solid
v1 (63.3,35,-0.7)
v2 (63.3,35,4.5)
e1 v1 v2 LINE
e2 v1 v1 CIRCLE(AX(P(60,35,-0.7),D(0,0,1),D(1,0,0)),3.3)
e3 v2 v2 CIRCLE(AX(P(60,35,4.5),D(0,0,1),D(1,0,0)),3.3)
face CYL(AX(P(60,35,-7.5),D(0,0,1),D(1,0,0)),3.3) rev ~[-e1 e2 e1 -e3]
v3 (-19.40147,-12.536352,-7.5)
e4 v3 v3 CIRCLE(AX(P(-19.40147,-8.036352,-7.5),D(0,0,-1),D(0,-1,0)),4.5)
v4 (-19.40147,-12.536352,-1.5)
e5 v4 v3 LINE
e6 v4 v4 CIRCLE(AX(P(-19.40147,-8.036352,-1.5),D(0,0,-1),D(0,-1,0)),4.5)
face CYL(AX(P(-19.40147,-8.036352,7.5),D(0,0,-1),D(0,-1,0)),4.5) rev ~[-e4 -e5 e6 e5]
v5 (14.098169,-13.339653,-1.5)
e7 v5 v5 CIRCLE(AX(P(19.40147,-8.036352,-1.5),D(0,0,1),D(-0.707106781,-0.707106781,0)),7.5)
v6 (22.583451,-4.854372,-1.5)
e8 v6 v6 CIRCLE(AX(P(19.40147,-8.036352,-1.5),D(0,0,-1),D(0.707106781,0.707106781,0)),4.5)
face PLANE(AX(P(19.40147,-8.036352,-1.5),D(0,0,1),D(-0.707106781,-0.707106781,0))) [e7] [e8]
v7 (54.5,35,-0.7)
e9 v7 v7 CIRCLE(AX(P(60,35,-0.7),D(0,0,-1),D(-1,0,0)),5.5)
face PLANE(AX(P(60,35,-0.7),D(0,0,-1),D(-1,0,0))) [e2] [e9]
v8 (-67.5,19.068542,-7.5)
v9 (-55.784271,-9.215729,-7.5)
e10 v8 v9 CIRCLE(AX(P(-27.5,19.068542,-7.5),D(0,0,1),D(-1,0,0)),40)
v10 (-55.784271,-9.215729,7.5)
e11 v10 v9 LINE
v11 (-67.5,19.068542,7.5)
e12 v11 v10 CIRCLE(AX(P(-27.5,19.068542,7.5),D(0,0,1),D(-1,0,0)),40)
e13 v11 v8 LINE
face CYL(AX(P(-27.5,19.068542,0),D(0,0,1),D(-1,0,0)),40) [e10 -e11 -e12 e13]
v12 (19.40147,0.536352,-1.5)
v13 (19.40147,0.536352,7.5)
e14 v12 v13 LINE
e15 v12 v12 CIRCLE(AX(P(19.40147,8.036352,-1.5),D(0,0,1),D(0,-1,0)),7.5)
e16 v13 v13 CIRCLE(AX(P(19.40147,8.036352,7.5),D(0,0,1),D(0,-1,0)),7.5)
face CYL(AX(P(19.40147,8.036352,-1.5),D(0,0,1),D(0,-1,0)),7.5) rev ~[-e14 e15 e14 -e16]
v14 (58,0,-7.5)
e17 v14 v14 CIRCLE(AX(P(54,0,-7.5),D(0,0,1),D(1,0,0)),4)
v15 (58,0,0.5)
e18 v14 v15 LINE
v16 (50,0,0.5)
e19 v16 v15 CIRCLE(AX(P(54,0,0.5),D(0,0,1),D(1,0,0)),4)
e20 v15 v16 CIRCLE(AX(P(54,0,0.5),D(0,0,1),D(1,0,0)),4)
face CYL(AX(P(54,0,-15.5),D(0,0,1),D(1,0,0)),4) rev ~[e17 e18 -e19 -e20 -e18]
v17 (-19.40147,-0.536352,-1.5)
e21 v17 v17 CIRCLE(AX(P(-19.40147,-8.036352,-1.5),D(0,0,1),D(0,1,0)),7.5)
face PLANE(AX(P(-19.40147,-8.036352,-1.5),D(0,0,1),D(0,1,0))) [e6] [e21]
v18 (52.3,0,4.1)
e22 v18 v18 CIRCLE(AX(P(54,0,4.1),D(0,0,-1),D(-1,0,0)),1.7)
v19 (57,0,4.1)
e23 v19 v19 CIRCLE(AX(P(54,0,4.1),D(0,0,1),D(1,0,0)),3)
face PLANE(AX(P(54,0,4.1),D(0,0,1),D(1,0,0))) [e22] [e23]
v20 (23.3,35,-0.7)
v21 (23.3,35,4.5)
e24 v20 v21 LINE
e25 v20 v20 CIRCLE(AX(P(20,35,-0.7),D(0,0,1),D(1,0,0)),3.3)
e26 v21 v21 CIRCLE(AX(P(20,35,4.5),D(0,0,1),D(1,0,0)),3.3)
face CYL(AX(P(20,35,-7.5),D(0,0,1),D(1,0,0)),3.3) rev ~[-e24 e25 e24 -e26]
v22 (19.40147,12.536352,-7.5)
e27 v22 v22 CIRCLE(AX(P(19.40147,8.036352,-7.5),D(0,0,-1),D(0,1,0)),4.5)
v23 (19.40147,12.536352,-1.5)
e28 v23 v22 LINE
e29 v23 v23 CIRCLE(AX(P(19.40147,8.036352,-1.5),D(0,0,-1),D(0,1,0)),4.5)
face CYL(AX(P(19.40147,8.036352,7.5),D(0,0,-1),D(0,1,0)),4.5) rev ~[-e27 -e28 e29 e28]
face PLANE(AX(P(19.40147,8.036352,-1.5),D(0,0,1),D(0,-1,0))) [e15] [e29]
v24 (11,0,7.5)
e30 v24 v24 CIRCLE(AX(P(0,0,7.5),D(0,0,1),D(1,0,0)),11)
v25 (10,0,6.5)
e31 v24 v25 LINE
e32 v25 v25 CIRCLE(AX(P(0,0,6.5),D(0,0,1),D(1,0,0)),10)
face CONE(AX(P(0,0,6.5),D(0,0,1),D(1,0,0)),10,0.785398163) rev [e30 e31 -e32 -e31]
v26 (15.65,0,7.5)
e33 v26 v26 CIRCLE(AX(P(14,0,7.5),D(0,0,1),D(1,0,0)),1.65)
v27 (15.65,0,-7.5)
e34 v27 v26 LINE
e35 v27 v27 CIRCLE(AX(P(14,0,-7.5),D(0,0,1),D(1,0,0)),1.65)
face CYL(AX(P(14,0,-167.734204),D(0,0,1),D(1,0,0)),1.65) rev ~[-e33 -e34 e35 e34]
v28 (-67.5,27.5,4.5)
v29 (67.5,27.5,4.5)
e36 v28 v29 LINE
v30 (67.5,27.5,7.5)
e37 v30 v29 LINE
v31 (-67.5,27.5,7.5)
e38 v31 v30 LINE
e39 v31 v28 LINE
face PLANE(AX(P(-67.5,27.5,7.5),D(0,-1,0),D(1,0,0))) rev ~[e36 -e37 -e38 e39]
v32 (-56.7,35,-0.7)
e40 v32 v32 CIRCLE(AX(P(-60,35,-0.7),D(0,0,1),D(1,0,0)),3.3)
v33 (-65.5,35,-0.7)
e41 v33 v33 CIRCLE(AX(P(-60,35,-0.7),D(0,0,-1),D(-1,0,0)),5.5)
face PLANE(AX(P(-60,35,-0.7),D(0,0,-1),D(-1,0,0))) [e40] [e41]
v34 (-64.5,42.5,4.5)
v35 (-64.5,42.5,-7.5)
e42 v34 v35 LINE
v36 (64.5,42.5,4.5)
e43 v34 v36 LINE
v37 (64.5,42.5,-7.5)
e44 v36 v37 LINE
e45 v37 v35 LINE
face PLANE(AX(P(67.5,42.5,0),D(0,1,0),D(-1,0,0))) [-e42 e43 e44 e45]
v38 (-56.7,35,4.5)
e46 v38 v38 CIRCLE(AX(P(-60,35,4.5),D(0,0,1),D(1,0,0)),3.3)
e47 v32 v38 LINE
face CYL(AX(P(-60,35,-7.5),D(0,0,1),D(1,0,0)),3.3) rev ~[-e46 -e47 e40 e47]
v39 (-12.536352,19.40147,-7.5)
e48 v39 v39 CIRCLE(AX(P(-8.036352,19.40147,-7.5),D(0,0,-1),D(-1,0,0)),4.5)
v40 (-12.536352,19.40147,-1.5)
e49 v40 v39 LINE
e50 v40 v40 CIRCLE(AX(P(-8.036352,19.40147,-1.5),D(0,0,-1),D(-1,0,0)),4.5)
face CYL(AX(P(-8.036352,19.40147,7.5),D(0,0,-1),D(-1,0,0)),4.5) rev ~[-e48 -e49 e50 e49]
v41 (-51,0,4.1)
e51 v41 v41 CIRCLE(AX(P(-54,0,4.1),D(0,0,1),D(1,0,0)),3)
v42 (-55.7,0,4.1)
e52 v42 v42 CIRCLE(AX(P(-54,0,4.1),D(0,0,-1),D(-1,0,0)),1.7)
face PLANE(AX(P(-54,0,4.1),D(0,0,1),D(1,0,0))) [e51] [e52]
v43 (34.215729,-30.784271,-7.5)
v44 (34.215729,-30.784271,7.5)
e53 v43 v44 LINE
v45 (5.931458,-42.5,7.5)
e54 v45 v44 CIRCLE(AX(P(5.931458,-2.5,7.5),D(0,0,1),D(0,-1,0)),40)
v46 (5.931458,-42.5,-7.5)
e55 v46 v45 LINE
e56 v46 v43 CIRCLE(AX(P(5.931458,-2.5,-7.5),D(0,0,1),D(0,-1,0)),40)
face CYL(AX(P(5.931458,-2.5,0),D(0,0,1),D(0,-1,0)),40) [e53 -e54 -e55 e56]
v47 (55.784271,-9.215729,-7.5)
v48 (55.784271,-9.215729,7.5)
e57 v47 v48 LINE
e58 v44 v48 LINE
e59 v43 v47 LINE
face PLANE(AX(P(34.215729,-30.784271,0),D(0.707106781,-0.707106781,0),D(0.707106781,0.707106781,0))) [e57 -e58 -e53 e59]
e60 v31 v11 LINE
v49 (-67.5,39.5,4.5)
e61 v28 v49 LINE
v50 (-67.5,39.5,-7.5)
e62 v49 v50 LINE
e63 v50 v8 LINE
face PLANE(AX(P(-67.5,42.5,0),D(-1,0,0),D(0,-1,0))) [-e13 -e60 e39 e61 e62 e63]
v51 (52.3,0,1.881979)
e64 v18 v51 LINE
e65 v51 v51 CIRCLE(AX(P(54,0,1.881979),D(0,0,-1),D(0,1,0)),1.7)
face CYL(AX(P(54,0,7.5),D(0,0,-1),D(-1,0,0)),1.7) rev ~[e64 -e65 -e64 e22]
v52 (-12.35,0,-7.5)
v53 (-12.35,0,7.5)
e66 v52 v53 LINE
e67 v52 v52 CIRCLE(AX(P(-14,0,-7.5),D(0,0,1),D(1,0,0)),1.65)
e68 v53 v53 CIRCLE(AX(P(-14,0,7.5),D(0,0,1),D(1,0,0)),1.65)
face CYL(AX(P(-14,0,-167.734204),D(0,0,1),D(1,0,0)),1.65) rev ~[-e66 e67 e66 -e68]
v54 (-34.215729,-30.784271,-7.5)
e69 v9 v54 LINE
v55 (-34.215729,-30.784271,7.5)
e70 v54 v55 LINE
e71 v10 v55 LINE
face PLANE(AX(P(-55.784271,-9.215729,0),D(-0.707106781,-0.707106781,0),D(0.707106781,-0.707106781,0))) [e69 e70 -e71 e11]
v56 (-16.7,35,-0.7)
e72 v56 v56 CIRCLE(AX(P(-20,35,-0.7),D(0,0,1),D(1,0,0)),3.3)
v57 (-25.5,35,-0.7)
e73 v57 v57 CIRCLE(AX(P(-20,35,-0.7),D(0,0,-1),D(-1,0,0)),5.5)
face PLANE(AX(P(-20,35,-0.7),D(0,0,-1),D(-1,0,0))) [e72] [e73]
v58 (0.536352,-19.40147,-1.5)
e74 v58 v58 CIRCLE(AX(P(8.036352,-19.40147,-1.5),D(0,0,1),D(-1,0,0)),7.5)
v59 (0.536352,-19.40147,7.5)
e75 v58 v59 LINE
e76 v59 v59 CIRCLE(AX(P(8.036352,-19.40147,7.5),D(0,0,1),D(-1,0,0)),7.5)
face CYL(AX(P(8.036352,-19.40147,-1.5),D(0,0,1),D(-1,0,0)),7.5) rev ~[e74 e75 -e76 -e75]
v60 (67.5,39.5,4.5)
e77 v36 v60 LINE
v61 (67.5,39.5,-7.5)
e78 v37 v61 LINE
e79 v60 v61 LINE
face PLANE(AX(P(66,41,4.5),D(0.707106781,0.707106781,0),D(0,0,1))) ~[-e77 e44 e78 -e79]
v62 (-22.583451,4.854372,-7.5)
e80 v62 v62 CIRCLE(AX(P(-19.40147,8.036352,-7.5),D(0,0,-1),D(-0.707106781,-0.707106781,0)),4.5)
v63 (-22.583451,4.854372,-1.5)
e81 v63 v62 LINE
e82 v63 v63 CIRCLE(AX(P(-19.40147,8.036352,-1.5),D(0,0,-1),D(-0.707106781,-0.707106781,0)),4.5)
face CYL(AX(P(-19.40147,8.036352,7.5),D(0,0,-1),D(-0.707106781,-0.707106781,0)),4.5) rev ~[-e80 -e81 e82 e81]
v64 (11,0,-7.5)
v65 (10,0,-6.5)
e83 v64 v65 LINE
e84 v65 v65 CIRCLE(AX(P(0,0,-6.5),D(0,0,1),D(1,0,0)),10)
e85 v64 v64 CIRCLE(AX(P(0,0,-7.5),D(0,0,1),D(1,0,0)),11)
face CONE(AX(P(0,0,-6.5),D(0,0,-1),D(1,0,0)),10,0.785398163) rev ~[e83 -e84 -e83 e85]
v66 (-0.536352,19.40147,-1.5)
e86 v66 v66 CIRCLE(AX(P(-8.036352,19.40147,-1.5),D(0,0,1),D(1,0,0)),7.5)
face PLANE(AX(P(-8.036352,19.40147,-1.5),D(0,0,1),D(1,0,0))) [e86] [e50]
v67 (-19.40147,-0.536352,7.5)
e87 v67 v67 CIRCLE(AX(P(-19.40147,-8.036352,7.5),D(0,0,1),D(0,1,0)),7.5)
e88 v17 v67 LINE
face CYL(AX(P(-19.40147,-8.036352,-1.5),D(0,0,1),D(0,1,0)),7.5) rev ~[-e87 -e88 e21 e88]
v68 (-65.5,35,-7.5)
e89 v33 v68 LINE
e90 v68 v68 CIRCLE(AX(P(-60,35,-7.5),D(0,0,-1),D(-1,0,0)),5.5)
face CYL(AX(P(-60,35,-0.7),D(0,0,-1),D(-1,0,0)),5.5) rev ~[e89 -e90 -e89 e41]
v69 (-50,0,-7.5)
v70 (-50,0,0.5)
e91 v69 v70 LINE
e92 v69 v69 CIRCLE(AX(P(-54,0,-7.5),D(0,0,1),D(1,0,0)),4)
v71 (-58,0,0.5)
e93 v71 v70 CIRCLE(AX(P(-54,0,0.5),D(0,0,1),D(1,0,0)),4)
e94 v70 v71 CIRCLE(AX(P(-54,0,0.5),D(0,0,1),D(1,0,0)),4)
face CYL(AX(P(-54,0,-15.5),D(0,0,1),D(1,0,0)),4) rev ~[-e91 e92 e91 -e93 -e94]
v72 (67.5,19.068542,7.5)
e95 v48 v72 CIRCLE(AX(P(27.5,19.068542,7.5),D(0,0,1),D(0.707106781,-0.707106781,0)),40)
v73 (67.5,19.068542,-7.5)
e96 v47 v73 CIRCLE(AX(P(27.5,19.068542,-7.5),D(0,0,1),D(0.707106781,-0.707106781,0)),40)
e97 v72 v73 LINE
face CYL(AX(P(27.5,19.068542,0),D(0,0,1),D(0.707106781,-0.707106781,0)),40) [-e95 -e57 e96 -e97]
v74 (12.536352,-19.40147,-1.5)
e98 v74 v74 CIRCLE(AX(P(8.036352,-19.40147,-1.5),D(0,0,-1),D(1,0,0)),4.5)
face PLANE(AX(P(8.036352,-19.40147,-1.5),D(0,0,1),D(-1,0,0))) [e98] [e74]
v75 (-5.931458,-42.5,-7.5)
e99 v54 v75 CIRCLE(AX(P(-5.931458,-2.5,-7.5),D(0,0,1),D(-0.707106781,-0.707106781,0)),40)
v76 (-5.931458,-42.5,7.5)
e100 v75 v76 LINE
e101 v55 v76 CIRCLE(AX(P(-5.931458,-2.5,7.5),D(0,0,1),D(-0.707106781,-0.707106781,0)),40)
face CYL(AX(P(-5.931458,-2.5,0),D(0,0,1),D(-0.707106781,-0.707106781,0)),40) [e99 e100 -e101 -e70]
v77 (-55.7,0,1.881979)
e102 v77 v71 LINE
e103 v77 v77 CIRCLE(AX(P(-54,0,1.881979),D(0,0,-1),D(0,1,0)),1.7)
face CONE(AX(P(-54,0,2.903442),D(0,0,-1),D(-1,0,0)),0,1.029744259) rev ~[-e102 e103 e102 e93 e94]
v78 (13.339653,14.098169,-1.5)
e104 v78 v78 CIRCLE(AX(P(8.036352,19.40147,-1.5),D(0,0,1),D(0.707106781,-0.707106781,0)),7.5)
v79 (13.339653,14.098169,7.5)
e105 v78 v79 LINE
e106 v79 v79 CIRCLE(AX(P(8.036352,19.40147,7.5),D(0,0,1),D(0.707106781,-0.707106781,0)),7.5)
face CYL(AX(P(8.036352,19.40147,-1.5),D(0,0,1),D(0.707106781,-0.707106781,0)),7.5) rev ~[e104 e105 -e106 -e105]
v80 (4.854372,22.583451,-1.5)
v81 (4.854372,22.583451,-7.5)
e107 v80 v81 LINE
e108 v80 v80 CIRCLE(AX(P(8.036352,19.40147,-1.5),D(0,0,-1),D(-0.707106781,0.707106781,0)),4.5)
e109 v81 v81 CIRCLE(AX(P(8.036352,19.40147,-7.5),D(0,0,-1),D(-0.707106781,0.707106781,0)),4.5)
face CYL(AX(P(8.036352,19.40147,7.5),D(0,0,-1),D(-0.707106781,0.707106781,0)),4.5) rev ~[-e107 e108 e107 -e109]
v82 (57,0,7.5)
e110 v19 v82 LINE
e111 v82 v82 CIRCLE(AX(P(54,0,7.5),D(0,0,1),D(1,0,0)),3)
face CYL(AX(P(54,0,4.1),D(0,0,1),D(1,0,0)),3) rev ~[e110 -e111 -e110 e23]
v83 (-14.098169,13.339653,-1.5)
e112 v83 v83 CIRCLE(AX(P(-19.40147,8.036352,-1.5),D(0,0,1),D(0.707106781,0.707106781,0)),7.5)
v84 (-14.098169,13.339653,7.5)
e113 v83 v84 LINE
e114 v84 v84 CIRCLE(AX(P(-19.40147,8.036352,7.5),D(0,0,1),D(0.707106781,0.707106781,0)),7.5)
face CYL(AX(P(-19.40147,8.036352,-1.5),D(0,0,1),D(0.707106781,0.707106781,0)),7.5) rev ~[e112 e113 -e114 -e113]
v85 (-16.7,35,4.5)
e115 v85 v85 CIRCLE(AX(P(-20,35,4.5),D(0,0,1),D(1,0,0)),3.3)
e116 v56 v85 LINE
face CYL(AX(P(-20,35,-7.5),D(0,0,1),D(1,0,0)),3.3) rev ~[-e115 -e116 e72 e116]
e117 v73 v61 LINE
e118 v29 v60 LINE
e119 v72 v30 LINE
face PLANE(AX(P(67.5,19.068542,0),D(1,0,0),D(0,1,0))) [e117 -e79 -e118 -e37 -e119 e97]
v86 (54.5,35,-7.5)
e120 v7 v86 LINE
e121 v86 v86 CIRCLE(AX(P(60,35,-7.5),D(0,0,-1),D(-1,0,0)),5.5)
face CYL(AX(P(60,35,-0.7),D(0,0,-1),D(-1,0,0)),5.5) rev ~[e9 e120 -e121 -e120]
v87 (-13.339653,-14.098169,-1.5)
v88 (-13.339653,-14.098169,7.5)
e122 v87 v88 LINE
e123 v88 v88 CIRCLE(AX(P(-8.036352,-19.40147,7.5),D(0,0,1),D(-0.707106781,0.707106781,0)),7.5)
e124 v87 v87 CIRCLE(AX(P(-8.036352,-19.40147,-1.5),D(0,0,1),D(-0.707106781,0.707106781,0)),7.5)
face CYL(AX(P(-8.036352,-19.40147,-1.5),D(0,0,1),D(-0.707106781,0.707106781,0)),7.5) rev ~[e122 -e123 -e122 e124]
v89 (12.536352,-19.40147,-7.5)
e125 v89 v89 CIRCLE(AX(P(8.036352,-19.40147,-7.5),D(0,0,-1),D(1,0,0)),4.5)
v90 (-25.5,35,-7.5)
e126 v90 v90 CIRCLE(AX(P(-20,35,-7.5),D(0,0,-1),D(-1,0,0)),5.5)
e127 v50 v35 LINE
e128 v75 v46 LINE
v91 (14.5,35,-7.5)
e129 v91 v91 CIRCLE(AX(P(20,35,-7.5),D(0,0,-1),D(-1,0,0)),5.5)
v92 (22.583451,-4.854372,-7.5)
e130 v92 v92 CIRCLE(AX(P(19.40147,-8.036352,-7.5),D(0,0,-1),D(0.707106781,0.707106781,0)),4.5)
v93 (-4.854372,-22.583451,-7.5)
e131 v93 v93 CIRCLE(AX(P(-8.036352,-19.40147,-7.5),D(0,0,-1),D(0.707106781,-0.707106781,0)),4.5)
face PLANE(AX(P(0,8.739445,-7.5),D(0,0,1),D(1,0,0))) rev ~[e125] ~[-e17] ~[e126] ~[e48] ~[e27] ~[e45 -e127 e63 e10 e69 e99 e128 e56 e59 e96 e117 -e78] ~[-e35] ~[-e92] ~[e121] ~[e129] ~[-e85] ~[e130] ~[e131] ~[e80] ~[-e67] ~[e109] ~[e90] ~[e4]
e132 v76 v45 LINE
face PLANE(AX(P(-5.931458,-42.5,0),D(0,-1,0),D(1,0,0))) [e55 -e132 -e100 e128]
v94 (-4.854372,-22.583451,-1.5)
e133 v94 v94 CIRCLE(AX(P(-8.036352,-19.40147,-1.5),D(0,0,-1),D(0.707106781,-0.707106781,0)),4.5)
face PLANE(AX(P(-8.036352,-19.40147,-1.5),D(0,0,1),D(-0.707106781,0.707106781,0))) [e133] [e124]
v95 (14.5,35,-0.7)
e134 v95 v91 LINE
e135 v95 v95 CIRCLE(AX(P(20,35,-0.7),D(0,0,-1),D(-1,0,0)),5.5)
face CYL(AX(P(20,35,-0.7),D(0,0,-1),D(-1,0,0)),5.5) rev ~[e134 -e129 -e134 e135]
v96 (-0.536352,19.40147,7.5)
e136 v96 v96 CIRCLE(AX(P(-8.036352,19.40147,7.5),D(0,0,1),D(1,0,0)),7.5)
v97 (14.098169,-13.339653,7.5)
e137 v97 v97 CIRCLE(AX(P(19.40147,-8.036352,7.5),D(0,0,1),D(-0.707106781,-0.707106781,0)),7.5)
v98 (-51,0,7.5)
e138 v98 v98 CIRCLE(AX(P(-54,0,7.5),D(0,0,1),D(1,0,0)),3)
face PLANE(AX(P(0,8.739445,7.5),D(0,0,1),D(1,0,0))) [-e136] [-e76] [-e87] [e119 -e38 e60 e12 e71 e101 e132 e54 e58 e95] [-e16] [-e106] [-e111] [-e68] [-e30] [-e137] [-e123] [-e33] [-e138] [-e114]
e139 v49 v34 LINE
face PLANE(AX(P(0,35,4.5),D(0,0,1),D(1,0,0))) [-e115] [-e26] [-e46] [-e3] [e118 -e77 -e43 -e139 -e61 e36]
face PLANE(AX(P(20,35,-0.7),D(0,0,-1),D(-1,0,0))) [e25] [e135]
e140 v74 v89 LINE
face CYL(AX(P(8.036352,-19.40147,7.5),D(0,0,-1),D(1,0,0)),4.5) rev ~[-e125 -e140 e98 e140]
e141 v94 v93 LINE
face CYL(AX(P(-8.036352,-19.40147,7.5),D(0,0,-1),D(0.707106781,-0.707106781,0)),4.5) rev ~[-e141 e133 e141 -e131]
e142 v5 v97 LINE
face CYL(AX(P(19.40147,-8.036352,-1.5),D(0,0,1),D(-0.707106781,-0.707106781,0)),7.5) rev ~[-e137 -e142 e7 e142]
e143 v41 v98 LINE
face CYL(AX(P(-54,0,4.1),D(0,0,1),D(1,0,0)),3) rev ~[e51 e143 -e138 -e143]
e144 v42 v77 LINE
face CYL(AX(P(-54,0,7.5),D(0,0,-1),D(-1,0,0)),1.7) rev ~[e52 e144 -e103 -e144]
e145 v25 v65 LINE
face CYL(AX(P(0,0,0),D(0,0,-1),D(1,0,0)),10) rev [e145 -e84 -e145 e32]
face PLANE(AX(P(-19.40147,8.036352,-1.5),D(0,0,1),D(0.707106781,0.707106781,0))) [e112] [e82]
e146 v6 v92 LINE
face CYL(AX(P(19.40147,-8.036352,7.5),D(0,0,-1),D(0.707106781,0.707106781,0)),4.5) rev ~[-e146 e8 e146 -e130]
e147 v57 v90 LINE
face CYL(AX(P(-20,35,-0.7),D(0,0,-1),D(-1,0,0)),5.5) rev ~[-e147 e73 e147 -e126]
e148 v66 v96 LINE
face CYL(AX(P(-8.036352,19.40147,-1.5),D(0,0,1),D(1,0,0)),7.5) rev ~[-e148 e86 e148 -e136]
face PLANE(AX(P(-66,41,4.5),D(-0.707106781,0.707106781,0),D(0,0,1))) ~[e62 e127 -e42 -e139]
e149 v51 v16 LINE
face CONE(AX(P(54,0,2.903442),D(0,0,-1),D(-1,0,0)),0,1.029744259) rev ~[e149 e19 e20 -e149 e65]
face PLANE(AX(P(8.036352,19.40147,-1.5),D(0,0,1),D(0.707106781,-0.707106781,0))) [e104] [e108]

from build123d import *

# Parameters (mm, degrees)
SKETCH_1_R                  = 10
EXTRUDE_1_DEPTH             = 7.5
HOLE_WIZARD_2_D             = 9
HOLE_WIZARD_2_CBORE_D       = 15
HOLE_WIZARD_2_CBORE_DEPTH   = 9
CHAMFER_1_SIZE              = 1
PATTERN_CIRCULAR_1_COUNT    = 8
HOLE_WIZARD_2_2_D           = 3.4
HOLE_WIZARD_2_2_CBORE_D     = 6
HOLE_WIZARD_2_2_CBORE_DEPTH = 3.4
HOLE_WIZARD_8_0_8_1_D       = 8
HOLE_WIZARD_8_0_8_1_DEPTH   = 8
HOLE_WIZARD_8_0_8_1_TIP     = 2.403442476
HOLE_WIZARD_M4_1_D          = 3.3
SKETCH_10_W                 = 135
SKETCH_10_H                 = 15
CUT_EXTRUDE_1_DEPTH         = 3
HOLE_WIZARD_3_D             = 6.6
HOLE_WIZARD_3_CBORE_D       = 11
HOLE_WIZARD_3_CBORE_DEPTH   = 6.8
CHAMFER_2_SIZE              = 3


with BuildPart() as part:
    # 草图1 → 凸台-拉伸1 (new, symmetric)
    with BuildSketch(Plane.XY):
        with BuildLine():
            Line((-55.784271247, -9.215728753), (-34.215728753, -30.784271247))
            ThreePointArc((-34.215728753, -30.784271247), (-21.2387948, -39.4551813), (-5.931457505, -42.5))
            Line((-5.931457505, -42.5), (5.931457505, -42.5))
            ThreePointArc((5.931457505, -42.5), (21.2387948, -39.4551813), (34.215728753, -30.784271247))
            Line((34.215728753, -30.784271247), (55.784271247, -9.215728753))
            ThreePointArc((55.784271247, -9.215728753), (64.4551813, 3.7612052), (67.5, 19.068542495))
            Line((67.5, 19.068542495), (67.5, 42.5))
            Line((67.5, 42.5), (-67.5, 42.5))
            Line((-67.5, 42.5), (-67.5, 19.068542495))
            ThreePointArc((-67.5, 19.068542495), (-64.4551813, 3.7612052), (-55.784271247, -9.215728753))
        make_face()
        Circle(SKETCH_1_R, mode=Mode.SUBTRACT)
    extrude(amount=EXTRUDE_1_DEPTH, both=True)

    # Hole Wizard 2 (through all)
    with Locations(Plane.XY.offset(7.5)):
        with Locations((-8.03635208, 19.401470183)):
            hole_wizard_2 = CounterBoreHole(HOLE_WIZARD_2_D / 2, HOLE_WIZARD_2_CBORE_D / 2, HOLE_WIZARD_2_CBORE_DEPTH)

    # 倒角1
    chamfer_1_edges = [part.edges().sort_by_distance(p)[0] for p in [
        (-10, 0, -7.5),
        (-10, 0, 7.5),
    ]]
    chamfer(chamfer_1_edges, length=CHAMFER_1_SIZE)

    # 阵列(圆周)1: Hole Wizard 2 ×8 about axis
    pattern_circular_1_axis = Axis((0, 0, 0), (0, 0, 1))
    for i in range(1, PATTERN_CIRCULAR_1_COUNT):
        add(hole_wizard_2.rotate(pattern_circular_1_axis, i * 360 / PATTERN_CIRCULAR_1_COUNT), mode=Mode.SUBTRACT)

    # Hole Wizard 2 2 (through all)
    with Locations(Plane.XY.offset(7.5)):
        with Locations((-54, 0), (54, 0)):
            CounterBoreHole(HOLE_WIZARD_2_2_D / 2, HOLE_WIZARD_2_2_CBORE_D / 2, HOLE_WIZARD_2_2_CBORE_DEPTH)

    # Ø8.0 (8) 直径孔1
    with Locations(Plane(origin=(0, 0, -7.5), x_dir=(-1, 0, 0), z_dir=(0, 0, -1))):
        with Locations((-54, 0), (54, 0)):
            Hole(HOLE_WIZARD_8_0_8_1_D / 2, depth=HOLE_WIZARD_8_0_8_1_DEPTH)
            with Locations((0, 0, -(HOLE_WIZARD_8_0_8_1_DEPTH + HOLE_WIZARD_8_0_8_1_TIP / 2))):  # 118° drill point
                Cone(0, HOLE_WIZARD_8_0_8_1_D / 2, HOLE_WIZARD_8_0_8_1_TIP, mode=Mode.SUBTRACT)

    # M4 螺纹孔1 (through all)
    with Locations(Plane(origin=(0, 0, -7.5), x_dir=(-1, 0, 0), z_dir=(0, 0, -1))):
        with Locations((-14, 0), (14, 0)):
            Hole(HOLE_WIZARD_M4_1_D / 2)

    # 草图10 → 切除-拉伸1 (cut)
    with BuildSketch(Plane.XY.offset(7.5)):
        with Locations((0, 35)):
            Rectangle(SKETCH_10_W, SKETCH_10_H)
    extrude(amount=-CUT_EXTRUDE_1_DEPTH, mode=Mode.SUBTRACT)

    # 打孔尺寸(%根据)内六角圆柱头螺钉的类型3 (through all)
    with Locations(Plane(origin=(0, 0, -7.5), x_dir=(-1, 0, 0), z_dir=(0, 0, -1))):
        with Locations((-20, 35), (-60, 35), (60, 35), (20, 35)):
            CounterBoreHole(HOLE_WIZARD_3_D / 2, HOLE_WIZARD_3_CBORE_D / 2, HOLE_WIZARD_3_CBORE_DEPTH)

    # 倒角2
    chamfer_2_edges = [part.edges().sort_by_distance(p)[0] for p in [
        (-67.5, 42.5, -1.5),
        (67.5, 42.5, -1.5),
    ]]
    chamfer(chamfer_2_edges, length=CHAMFER_2_SIZE)


solid = part.part
